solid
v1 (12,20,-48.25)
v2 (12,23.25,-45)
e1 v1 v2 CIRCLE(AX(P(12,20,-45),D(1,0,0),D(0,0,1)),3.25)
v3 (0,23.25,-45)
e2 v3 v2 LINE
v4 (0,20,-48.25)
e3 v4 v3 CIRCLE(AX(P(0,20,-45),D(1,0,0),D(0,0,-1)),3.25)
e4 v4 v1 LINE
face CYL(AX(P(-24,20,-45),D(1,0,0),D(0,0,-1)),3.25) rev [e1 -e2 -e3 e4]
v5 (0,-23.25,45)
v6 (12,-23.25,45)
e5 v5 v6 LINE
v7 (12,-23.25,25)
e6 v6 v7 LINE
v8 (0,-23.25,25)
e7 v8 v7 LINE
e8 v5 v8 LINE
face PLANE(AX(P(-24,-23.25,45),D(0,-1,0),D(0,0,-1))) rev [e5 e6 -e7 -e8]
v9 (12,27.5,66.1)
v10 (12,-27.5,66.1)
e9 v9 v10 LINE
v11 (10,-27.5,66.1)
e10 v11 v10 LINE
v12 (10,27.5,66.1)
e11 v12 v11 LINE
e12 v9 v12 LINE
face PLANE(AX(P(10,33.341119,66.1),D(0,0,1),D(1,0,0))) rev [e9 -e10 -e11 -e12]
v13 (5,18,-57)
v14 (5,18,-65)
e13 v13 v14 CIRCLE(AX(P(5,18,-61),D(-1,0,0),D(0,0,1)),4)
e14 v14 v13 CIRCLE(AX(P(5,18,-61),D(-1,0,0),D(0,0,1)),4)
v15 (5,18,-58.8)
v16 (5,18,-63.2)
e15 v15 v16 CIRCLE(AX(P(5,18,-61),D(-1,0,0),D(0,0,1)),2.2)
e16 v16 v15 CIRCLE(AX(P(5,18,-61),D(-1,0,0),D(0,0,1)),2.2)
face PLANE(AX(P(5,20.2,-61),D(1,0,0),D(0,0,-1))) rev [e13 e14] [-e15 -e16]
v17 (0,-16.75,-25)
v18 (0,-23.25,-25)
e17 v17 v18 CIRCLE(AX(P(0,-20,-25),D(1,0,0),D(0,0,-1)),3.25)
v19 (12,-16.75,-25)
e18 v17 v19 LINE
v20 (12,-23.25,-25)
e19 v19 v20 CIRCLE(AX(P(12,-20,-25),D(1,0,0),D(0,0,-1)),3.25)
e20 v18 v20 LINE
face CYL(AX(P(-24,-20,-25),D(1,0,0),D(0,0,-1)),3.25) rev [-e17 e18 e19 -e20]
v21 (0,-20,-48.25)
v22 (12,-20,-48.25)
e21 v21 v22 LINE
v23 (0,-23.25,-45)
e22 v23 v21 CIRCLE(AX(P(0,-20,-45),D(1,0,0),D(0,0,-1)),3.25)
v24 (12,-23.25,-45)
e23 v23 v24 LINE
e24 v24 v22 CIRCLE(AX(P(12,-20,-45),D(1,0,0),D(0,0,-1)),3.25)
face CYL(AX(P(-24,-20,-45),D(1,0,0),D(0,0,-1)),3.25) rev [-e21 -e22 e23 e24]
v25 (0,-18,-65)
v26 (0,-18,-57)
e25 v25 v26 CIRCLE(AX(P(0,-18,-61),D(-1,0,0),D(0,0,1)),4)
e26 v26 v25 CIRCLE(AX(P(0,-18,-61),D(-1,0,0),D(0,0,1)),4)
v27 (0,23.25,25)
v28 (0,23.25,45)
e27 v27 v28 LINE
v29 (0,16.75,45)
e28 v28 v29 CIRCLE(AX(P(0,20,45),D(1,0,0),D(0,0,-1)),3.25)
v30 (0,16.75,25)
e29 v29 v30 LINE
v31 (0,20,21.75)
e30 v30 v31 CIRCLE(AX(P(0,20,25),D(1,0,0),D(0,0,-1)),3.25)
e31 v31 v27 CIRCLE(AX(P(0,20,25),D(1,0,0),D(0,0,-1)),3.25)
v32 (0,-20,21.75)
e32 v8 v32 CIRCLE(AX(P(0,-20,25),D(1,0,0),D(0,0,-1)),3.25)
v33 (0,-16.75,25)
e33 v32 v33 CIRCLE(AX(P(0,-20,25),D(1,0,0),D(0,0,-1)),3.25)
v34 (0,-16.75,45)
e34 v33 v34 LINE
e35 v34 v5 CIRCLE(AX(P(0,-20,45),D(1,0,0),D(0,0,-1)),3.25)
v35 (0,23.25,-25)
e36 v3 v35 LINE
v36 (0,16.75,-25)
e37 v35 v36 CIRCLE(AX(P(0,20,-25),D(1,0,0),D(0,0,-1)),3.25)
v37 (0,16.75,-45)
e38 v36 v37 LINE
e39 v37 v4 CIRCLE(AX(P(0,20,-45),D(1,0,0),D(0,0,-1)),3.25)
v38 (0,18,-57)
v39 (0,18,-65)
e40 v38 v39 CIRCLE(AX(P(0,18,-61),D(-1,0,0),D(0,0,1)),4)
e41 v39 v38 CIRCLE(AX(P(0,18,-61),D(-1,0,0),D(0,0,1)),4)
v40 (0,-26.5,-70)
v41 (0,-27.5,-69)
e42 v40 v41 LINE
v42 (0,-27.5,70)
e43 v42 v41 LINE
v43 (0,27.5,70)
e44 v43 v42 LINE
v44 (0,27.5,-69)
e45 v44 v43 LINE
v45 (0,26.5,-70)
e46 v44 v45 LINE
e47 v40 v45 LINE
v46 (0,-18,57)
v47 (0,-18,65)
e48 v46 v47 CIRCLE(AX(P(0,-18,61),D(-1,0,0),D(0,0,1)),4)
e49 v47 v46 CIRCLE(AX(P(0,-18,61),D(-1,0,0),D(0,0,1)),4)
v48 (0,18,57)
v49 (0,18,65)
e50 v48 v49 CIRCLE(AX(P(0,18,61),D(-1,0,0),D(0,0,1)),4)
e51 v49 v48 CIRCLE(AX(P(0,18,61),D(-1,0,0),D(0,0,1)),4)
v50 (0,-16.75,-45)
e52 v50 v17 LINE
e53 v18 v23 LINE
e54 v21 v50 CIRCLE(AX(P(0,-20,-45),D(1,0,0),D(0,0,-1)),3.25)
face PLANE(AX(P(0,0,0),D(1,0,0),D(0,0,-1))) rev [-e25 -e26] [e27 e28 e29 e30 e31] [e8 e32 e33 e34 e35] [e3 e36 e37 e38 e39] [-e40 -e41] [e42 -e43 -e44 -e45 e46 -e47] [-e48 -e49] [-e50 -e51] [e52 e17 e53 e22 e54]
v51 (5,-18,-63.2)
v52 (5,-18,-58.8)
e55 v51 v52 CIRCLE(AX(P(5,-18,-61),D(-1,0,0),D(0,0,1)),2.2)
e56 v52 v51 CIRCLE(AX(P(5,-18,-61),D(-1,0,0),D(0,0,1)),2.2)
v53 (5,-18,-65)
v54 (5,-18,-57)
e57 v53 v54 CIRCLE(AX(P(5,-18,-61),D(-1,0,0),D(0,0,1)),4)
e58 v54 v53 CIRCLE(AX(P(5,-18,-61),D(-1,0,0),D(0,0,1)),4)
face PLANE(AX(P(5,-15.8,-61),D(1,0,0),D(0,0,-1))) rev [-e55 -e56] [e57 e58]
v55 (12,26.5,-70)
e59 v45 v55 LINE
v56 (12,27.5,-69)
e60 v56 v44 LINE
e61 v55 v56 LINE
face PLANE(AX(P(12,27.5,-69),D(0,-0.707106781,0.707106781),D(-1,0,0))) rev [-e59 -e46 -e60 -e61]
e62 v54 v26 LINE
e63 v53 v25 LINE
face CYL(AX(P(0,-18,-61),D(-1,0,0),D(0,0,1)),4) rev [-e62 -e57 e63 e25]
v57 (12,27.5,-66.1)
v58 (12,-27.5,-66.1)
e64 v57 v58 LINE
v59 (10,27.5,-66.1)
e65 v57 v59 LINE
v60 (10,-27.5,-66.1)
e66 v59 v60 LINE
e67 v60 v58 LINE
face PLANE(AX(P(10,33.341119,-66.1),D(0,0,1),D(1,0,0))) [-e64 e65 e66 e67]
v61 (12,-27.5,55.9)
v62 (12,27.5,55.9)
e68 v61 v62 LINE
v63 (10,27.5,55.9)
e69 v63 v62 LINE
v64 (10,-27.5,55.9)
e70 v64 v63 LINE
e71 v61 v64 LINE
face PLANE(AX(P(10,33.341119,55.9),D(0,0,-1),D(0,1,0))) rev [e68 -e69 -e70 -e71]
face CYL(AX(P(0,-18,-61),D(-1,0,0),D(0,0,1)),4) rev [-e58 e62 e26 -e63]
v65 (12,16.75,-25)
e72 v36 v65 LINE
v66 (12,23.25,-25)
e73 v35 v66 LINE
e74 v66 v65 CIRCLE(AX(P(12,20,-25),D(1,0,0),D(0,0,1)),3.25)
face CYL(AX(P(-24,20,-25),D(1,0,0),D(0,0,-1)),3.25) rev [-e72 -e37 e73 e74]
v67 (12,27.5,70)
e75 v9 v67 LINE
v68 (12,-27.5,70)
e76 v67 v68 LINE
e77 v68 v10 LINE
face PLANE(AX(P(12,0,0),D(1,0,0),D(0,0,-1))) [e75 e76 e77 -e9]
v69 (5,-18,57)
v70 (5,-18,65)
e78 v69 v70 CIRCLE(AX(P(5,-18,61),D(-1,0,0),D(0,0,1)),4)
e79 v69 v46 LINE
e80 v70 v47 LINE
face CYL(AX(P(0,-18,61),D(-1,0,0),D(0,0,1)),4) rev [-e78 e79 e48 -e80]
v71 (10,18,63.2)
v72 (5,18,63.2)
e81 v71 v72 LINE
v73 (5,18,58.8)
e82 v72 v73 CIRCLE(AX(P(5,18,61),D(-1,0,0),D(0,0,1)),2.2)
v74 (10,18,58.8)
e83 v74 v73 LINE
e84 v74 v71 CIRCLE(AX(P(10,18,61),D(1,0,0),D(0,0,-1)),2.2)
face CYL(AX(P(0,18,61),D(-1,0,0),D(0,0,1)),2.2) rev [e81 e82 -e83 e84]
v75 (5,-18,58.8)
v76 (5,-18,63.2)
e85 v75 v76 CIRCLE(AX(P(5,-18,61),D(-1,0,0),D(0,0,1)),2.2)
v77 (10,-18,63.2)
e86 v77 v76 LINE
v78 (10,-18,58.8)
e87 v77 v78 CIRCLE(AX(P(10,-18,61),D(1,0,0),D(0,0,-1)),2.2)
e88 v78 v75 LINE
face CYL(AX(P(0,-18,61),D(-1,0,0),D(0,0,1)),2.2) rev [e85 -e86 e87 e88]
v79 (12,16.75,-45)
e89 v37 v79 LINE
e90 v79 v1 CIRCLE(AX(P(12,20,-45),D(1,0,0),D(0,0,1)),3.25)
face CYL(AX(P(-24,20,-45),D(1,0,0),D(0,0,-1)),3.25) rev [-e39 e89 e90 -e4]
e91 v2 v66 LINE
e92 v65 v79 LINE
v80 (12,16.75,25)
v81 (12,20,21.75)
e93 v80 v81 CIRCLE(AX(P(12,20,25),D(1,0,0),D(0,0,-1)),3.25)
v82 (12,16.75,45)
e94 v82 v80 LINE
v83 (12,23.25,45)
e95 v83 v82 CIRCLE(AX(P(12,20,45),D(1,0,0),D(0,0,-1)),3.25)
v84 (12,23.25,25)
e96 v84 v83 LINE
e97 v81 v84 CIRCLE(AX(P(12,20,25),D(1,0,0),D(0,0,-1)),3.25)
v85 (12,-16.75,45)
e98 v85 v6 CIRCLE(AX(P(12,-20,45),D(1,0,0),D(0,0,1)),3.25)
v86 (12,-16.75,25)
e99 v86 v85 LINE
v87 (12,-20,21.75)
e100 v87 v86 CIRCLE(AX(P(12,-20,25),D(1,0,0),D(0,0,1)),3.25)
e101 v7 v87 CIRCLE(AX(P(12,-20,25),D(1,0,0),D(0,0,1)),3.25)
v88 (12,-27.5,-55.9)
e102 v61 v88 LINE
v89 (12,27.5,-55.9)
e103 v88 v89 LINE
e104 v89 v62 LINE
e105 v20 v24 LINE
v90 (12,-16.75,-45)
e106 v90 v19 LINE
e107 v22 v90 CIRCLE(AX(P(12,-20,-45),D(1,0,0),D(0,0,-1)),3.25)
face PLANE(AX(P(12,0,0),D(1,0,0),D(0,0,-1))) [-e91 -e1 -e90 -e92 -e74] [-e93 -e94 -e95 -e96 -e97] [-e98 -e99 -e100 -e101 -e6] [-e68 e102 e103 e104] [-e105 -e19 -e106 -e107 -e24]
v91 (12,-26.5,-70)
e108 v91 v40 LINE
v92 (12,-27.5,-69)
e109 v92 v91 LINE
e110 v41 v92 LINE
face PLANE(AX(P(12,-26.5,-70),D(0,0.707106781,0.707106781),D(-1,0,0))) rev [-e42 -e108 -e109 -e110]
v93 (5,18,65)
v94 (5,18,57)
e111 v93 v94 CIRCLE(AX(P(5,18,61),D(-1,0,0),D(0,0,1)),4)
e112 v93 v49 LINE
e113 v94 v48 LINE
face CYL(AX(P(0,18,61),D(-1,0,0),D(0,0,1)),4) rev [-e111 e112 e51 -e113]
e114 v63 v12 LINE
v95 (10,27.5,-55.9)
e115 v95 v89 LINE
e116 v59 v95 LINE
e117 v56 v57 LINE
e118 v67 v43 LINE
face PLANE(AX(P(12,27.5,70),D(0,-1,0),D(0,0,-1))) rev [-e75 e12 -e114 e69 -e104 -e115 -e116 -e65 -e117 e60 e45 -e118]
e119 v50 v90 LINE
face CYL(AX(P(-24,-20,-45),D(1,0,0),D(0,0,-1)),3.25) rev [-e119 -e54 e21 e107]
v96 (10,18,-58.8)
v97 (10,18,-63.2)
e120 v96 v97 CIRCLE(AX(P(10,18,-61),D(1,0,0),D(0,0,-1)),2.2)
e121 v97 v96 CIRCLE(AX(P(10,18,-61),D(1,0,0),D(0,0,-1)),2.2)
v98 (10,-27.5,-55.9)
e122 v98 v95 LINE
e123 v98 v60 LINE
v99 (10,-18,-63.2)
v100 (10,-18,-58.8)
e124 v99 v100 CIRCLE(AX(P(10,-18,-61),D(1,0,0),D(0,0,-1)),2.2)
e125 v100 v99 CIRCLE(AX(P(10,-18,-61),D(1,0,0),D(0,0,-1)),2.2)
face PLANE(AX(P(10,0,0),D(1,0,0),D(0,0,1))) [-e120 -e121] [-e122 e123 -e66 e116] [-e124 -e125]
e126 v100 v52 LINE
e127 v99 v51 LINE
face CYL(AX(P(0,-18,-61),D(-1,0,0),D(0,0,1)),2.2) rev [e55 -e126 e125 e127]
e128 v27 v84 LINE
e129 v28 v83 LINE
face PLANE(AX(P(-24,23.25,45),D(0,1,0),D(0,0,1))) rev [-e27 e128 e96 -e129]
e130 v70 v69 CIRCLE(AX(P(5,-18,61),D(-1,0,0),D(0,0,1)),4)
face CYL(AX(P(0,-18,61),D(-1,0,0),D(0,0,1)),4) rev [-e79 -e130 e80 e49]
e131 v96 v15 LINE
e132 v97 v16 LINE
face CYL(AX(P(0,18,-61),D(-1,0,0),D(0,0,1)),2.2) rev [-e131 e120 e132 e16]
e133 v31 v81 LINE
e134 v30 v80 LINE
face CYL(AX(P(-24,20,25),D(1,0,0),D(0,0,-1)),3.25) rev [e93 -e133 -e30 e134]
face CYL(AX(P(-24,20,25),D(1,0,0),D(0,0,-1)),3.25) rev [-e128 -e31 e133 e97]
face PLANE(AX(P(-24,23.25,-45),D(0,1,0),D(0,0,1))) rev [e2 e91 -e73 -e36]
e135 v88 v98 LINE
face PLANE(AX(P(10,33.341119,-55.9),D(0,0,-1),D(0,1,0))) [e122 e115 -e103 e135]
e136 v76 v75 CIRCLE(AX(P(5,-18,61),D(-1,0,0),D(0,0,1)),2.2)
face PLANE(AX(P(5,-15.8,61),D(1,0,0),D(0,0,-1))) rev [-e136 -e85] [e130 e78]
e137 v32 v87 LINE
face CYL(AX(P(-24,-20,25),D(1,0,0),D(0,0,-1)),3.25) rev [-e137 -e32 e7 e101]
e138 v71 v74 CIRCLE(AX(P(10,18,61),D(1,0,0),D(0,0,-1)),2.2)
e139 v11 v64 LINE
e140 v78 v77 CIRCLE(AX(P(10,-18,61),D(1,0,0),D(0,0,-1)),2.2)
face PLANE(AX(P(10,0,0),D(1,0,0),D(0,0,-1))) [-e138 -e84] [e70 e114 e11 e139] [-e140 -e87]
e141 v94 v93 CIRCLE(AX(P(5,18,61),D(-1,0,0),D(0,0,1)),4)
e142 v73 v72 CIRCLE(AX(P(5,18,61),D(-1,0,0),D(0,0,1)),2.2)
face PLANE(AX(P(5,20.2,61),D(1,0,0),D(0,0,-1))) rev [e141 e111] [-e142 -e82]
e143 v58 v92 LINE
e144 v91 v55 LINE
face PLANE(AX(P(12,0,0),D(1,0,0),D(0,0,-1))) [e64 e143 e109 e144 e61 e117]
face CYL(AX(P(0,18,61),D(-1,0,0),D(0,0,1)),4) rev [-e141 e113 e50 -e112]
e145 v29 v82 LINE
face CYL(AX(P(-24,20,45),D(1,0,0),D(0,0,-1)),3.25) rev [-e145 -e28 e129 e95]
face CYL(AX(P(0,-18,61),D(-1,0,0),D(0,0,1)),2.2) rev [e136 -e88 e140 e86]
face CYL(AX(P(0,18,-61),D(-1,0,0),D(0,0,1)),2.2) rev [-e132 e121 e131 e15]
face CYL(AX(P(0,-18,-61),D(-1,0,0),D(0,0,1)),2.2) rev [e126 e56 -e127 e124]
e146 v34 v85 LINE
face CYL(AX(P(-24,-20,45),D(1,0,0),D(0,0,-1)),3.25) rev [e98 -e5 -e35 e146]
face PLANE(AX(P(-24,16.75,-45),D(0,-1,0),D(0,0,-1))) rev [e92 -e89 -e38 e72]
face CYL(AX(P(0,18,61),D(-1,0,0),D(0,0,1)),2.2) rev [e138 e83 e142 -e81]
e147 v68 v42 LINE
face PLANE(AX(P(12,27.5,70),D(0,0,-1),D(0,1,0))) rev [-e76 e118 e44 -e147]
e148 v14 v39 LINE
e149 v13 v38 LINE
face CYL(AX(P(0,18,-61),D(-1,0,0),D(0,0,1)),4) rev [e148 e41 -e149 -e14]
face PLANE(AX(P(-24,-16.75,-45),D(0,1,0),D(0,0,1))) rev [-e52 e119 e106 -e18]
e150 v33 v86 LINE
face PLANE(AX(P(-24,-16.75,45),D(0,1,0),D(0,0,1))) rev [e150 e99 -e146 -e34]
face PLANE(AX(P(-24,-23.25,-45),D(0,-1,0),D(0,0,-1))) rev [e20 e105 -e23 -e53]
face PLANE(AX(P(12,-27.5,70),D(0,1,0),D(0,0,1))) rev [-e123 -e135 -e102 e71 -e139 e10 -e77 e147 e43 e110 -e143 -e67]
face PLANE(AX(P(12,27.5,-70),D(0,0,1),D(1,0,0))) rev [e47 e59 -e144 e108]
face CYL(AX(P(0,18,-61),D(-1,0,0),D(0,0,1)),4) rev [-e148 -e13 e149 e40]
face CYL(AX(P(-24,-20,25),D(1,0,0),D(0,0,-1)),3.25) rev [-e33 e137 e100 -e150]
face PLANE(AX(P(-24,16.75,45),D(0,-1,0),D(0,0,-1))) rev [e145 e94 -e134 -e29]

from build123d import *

# Parameters (mm, degrees)
SKETCH_1_W                = 140
SKETCH_1_H                = 55
EXTRUDE_1_DEPTH           = 12
SKETCH_2_W                = 10.2
SKETCH_2_H                = 67.741828953
CUT_EXTRUDE_1_DEPTH       = 2
CHAMFER_1_SIZE            = 1
CUT_EXTRUDE_2_DEPTH       = 36
HOLE_WIZARD_0_D           = 4.4
HOLE_WIZARD_0_CBORE_D     = 8
HOLE_WIZARD_0_CBORE_DEPTH = 5


with BuildPart() as part:
    # 草图1 → 凸台-拉伸1 (new body)
    with BuildSketch(Plane(origin=(0, 0, 0), x_dir=(0, 0, -1), z_dir=(1, 0, 0))):
        Rectangle(SKETCH_1_W, SKETCH_1_H)
    extrude(amount=EXTRUDE_1_DEPTH)

    # 草图2 → 切除-拉伸1 (cut)
    with BuildSketch(Plane(origin=(12, 0, 0), x_dir=(0, 0, -1), z_dir=(1, 0, 0))):
        with Locations((-61, -0.529795054)):
            Rectangle(SKETCH_2_W, SKETCH_2_H)
    cut_extrude_1 = extrude(amount=-CUT_EXTRUDE_1_DEPTH, mode=Mode.SUBTRACT)

    # 倒角1
    chamfer_1_edges = [part.edges().sort_by_distance(p)[0] for p in [
        (6, -27.5, -70),
        (6, 27.5, -70),
    ]]
    chamfer(chamfer_1_edges, length=CHAMFER_1_SIZE)

    # 镜向2: 切除-拉伸1 across plane
    add(cut_extrude_1.mirror(Plane.XY), mode=Mode.SUBTRACT)

    # 草图3 → 切除-拉伸2 (cut)
    with BuildSketch(Plane(origin=(12, 0, 0), x_dir=(0, 0, -1), z_dir=(1, 0, 0))):
        with BuildLine():
            Line((-45, 23.25), (-25, 23.25))
            ThreePointArc((-25, 23.25), (-21.75, 20), (-25, 16.75))
            Line((-25, 16.75), (-45, 16.75))
            ThreePointArc((-45, 16.75), (-48.25, 20), (-45, 23.25))
        make_face()
        with BuildLine():
            Line((-45, -23.25), (-25, -23.25))
            ThreePointArc((-25, -23.25), (-21.75, -20), (-25, -16.75))
            Line((-25, -16.75), (-45, -16.75))
            ThreePointArc((-45, -16.75), (-48.25, -20), (-45, -23.25))
        make_face()
        with BuildLine():
            Line((45, 23.25), (25, 23.25))
            ThreePointArc((25, 23.25), (21.75, 20), (25, 16.75))
            Line((25, 16.75), (45, 16.75))
            ThreePointArc((45, 16.75), (48.25, 20), (45, 23.25))
        make_face()
        with BuildLine():
            Line((45, -23.25), (25, -23.25))
            ThreePointArc((25, -23.25), (21.75, -20), (25, -16.75))
            Line((25, -16.75), (45, -16.75))
            ThreePointArc((45, -16.75), (48.25, -20), (45, -23.25))
        make_face()
    extrude(amount=-CUT_EXTRUDE_2_DEPTH, mode=Mode.SUBTRACT)

    # 打孔尺寸(%根据)内六角圆柱头螺钉的类型0 (through all)
    with Locations(Plane.ZY):
        with Locations((-61, 18), (-61, -18), (61, 18), (61, -18)):
            CounterBoreHole(HOLE_WIZARD_0_D / 2, HOLE_WIZARD_0_CBORE_D / 2, HOLE_WIZARD_0_CBORE_DEPTH)


solid = part.part
